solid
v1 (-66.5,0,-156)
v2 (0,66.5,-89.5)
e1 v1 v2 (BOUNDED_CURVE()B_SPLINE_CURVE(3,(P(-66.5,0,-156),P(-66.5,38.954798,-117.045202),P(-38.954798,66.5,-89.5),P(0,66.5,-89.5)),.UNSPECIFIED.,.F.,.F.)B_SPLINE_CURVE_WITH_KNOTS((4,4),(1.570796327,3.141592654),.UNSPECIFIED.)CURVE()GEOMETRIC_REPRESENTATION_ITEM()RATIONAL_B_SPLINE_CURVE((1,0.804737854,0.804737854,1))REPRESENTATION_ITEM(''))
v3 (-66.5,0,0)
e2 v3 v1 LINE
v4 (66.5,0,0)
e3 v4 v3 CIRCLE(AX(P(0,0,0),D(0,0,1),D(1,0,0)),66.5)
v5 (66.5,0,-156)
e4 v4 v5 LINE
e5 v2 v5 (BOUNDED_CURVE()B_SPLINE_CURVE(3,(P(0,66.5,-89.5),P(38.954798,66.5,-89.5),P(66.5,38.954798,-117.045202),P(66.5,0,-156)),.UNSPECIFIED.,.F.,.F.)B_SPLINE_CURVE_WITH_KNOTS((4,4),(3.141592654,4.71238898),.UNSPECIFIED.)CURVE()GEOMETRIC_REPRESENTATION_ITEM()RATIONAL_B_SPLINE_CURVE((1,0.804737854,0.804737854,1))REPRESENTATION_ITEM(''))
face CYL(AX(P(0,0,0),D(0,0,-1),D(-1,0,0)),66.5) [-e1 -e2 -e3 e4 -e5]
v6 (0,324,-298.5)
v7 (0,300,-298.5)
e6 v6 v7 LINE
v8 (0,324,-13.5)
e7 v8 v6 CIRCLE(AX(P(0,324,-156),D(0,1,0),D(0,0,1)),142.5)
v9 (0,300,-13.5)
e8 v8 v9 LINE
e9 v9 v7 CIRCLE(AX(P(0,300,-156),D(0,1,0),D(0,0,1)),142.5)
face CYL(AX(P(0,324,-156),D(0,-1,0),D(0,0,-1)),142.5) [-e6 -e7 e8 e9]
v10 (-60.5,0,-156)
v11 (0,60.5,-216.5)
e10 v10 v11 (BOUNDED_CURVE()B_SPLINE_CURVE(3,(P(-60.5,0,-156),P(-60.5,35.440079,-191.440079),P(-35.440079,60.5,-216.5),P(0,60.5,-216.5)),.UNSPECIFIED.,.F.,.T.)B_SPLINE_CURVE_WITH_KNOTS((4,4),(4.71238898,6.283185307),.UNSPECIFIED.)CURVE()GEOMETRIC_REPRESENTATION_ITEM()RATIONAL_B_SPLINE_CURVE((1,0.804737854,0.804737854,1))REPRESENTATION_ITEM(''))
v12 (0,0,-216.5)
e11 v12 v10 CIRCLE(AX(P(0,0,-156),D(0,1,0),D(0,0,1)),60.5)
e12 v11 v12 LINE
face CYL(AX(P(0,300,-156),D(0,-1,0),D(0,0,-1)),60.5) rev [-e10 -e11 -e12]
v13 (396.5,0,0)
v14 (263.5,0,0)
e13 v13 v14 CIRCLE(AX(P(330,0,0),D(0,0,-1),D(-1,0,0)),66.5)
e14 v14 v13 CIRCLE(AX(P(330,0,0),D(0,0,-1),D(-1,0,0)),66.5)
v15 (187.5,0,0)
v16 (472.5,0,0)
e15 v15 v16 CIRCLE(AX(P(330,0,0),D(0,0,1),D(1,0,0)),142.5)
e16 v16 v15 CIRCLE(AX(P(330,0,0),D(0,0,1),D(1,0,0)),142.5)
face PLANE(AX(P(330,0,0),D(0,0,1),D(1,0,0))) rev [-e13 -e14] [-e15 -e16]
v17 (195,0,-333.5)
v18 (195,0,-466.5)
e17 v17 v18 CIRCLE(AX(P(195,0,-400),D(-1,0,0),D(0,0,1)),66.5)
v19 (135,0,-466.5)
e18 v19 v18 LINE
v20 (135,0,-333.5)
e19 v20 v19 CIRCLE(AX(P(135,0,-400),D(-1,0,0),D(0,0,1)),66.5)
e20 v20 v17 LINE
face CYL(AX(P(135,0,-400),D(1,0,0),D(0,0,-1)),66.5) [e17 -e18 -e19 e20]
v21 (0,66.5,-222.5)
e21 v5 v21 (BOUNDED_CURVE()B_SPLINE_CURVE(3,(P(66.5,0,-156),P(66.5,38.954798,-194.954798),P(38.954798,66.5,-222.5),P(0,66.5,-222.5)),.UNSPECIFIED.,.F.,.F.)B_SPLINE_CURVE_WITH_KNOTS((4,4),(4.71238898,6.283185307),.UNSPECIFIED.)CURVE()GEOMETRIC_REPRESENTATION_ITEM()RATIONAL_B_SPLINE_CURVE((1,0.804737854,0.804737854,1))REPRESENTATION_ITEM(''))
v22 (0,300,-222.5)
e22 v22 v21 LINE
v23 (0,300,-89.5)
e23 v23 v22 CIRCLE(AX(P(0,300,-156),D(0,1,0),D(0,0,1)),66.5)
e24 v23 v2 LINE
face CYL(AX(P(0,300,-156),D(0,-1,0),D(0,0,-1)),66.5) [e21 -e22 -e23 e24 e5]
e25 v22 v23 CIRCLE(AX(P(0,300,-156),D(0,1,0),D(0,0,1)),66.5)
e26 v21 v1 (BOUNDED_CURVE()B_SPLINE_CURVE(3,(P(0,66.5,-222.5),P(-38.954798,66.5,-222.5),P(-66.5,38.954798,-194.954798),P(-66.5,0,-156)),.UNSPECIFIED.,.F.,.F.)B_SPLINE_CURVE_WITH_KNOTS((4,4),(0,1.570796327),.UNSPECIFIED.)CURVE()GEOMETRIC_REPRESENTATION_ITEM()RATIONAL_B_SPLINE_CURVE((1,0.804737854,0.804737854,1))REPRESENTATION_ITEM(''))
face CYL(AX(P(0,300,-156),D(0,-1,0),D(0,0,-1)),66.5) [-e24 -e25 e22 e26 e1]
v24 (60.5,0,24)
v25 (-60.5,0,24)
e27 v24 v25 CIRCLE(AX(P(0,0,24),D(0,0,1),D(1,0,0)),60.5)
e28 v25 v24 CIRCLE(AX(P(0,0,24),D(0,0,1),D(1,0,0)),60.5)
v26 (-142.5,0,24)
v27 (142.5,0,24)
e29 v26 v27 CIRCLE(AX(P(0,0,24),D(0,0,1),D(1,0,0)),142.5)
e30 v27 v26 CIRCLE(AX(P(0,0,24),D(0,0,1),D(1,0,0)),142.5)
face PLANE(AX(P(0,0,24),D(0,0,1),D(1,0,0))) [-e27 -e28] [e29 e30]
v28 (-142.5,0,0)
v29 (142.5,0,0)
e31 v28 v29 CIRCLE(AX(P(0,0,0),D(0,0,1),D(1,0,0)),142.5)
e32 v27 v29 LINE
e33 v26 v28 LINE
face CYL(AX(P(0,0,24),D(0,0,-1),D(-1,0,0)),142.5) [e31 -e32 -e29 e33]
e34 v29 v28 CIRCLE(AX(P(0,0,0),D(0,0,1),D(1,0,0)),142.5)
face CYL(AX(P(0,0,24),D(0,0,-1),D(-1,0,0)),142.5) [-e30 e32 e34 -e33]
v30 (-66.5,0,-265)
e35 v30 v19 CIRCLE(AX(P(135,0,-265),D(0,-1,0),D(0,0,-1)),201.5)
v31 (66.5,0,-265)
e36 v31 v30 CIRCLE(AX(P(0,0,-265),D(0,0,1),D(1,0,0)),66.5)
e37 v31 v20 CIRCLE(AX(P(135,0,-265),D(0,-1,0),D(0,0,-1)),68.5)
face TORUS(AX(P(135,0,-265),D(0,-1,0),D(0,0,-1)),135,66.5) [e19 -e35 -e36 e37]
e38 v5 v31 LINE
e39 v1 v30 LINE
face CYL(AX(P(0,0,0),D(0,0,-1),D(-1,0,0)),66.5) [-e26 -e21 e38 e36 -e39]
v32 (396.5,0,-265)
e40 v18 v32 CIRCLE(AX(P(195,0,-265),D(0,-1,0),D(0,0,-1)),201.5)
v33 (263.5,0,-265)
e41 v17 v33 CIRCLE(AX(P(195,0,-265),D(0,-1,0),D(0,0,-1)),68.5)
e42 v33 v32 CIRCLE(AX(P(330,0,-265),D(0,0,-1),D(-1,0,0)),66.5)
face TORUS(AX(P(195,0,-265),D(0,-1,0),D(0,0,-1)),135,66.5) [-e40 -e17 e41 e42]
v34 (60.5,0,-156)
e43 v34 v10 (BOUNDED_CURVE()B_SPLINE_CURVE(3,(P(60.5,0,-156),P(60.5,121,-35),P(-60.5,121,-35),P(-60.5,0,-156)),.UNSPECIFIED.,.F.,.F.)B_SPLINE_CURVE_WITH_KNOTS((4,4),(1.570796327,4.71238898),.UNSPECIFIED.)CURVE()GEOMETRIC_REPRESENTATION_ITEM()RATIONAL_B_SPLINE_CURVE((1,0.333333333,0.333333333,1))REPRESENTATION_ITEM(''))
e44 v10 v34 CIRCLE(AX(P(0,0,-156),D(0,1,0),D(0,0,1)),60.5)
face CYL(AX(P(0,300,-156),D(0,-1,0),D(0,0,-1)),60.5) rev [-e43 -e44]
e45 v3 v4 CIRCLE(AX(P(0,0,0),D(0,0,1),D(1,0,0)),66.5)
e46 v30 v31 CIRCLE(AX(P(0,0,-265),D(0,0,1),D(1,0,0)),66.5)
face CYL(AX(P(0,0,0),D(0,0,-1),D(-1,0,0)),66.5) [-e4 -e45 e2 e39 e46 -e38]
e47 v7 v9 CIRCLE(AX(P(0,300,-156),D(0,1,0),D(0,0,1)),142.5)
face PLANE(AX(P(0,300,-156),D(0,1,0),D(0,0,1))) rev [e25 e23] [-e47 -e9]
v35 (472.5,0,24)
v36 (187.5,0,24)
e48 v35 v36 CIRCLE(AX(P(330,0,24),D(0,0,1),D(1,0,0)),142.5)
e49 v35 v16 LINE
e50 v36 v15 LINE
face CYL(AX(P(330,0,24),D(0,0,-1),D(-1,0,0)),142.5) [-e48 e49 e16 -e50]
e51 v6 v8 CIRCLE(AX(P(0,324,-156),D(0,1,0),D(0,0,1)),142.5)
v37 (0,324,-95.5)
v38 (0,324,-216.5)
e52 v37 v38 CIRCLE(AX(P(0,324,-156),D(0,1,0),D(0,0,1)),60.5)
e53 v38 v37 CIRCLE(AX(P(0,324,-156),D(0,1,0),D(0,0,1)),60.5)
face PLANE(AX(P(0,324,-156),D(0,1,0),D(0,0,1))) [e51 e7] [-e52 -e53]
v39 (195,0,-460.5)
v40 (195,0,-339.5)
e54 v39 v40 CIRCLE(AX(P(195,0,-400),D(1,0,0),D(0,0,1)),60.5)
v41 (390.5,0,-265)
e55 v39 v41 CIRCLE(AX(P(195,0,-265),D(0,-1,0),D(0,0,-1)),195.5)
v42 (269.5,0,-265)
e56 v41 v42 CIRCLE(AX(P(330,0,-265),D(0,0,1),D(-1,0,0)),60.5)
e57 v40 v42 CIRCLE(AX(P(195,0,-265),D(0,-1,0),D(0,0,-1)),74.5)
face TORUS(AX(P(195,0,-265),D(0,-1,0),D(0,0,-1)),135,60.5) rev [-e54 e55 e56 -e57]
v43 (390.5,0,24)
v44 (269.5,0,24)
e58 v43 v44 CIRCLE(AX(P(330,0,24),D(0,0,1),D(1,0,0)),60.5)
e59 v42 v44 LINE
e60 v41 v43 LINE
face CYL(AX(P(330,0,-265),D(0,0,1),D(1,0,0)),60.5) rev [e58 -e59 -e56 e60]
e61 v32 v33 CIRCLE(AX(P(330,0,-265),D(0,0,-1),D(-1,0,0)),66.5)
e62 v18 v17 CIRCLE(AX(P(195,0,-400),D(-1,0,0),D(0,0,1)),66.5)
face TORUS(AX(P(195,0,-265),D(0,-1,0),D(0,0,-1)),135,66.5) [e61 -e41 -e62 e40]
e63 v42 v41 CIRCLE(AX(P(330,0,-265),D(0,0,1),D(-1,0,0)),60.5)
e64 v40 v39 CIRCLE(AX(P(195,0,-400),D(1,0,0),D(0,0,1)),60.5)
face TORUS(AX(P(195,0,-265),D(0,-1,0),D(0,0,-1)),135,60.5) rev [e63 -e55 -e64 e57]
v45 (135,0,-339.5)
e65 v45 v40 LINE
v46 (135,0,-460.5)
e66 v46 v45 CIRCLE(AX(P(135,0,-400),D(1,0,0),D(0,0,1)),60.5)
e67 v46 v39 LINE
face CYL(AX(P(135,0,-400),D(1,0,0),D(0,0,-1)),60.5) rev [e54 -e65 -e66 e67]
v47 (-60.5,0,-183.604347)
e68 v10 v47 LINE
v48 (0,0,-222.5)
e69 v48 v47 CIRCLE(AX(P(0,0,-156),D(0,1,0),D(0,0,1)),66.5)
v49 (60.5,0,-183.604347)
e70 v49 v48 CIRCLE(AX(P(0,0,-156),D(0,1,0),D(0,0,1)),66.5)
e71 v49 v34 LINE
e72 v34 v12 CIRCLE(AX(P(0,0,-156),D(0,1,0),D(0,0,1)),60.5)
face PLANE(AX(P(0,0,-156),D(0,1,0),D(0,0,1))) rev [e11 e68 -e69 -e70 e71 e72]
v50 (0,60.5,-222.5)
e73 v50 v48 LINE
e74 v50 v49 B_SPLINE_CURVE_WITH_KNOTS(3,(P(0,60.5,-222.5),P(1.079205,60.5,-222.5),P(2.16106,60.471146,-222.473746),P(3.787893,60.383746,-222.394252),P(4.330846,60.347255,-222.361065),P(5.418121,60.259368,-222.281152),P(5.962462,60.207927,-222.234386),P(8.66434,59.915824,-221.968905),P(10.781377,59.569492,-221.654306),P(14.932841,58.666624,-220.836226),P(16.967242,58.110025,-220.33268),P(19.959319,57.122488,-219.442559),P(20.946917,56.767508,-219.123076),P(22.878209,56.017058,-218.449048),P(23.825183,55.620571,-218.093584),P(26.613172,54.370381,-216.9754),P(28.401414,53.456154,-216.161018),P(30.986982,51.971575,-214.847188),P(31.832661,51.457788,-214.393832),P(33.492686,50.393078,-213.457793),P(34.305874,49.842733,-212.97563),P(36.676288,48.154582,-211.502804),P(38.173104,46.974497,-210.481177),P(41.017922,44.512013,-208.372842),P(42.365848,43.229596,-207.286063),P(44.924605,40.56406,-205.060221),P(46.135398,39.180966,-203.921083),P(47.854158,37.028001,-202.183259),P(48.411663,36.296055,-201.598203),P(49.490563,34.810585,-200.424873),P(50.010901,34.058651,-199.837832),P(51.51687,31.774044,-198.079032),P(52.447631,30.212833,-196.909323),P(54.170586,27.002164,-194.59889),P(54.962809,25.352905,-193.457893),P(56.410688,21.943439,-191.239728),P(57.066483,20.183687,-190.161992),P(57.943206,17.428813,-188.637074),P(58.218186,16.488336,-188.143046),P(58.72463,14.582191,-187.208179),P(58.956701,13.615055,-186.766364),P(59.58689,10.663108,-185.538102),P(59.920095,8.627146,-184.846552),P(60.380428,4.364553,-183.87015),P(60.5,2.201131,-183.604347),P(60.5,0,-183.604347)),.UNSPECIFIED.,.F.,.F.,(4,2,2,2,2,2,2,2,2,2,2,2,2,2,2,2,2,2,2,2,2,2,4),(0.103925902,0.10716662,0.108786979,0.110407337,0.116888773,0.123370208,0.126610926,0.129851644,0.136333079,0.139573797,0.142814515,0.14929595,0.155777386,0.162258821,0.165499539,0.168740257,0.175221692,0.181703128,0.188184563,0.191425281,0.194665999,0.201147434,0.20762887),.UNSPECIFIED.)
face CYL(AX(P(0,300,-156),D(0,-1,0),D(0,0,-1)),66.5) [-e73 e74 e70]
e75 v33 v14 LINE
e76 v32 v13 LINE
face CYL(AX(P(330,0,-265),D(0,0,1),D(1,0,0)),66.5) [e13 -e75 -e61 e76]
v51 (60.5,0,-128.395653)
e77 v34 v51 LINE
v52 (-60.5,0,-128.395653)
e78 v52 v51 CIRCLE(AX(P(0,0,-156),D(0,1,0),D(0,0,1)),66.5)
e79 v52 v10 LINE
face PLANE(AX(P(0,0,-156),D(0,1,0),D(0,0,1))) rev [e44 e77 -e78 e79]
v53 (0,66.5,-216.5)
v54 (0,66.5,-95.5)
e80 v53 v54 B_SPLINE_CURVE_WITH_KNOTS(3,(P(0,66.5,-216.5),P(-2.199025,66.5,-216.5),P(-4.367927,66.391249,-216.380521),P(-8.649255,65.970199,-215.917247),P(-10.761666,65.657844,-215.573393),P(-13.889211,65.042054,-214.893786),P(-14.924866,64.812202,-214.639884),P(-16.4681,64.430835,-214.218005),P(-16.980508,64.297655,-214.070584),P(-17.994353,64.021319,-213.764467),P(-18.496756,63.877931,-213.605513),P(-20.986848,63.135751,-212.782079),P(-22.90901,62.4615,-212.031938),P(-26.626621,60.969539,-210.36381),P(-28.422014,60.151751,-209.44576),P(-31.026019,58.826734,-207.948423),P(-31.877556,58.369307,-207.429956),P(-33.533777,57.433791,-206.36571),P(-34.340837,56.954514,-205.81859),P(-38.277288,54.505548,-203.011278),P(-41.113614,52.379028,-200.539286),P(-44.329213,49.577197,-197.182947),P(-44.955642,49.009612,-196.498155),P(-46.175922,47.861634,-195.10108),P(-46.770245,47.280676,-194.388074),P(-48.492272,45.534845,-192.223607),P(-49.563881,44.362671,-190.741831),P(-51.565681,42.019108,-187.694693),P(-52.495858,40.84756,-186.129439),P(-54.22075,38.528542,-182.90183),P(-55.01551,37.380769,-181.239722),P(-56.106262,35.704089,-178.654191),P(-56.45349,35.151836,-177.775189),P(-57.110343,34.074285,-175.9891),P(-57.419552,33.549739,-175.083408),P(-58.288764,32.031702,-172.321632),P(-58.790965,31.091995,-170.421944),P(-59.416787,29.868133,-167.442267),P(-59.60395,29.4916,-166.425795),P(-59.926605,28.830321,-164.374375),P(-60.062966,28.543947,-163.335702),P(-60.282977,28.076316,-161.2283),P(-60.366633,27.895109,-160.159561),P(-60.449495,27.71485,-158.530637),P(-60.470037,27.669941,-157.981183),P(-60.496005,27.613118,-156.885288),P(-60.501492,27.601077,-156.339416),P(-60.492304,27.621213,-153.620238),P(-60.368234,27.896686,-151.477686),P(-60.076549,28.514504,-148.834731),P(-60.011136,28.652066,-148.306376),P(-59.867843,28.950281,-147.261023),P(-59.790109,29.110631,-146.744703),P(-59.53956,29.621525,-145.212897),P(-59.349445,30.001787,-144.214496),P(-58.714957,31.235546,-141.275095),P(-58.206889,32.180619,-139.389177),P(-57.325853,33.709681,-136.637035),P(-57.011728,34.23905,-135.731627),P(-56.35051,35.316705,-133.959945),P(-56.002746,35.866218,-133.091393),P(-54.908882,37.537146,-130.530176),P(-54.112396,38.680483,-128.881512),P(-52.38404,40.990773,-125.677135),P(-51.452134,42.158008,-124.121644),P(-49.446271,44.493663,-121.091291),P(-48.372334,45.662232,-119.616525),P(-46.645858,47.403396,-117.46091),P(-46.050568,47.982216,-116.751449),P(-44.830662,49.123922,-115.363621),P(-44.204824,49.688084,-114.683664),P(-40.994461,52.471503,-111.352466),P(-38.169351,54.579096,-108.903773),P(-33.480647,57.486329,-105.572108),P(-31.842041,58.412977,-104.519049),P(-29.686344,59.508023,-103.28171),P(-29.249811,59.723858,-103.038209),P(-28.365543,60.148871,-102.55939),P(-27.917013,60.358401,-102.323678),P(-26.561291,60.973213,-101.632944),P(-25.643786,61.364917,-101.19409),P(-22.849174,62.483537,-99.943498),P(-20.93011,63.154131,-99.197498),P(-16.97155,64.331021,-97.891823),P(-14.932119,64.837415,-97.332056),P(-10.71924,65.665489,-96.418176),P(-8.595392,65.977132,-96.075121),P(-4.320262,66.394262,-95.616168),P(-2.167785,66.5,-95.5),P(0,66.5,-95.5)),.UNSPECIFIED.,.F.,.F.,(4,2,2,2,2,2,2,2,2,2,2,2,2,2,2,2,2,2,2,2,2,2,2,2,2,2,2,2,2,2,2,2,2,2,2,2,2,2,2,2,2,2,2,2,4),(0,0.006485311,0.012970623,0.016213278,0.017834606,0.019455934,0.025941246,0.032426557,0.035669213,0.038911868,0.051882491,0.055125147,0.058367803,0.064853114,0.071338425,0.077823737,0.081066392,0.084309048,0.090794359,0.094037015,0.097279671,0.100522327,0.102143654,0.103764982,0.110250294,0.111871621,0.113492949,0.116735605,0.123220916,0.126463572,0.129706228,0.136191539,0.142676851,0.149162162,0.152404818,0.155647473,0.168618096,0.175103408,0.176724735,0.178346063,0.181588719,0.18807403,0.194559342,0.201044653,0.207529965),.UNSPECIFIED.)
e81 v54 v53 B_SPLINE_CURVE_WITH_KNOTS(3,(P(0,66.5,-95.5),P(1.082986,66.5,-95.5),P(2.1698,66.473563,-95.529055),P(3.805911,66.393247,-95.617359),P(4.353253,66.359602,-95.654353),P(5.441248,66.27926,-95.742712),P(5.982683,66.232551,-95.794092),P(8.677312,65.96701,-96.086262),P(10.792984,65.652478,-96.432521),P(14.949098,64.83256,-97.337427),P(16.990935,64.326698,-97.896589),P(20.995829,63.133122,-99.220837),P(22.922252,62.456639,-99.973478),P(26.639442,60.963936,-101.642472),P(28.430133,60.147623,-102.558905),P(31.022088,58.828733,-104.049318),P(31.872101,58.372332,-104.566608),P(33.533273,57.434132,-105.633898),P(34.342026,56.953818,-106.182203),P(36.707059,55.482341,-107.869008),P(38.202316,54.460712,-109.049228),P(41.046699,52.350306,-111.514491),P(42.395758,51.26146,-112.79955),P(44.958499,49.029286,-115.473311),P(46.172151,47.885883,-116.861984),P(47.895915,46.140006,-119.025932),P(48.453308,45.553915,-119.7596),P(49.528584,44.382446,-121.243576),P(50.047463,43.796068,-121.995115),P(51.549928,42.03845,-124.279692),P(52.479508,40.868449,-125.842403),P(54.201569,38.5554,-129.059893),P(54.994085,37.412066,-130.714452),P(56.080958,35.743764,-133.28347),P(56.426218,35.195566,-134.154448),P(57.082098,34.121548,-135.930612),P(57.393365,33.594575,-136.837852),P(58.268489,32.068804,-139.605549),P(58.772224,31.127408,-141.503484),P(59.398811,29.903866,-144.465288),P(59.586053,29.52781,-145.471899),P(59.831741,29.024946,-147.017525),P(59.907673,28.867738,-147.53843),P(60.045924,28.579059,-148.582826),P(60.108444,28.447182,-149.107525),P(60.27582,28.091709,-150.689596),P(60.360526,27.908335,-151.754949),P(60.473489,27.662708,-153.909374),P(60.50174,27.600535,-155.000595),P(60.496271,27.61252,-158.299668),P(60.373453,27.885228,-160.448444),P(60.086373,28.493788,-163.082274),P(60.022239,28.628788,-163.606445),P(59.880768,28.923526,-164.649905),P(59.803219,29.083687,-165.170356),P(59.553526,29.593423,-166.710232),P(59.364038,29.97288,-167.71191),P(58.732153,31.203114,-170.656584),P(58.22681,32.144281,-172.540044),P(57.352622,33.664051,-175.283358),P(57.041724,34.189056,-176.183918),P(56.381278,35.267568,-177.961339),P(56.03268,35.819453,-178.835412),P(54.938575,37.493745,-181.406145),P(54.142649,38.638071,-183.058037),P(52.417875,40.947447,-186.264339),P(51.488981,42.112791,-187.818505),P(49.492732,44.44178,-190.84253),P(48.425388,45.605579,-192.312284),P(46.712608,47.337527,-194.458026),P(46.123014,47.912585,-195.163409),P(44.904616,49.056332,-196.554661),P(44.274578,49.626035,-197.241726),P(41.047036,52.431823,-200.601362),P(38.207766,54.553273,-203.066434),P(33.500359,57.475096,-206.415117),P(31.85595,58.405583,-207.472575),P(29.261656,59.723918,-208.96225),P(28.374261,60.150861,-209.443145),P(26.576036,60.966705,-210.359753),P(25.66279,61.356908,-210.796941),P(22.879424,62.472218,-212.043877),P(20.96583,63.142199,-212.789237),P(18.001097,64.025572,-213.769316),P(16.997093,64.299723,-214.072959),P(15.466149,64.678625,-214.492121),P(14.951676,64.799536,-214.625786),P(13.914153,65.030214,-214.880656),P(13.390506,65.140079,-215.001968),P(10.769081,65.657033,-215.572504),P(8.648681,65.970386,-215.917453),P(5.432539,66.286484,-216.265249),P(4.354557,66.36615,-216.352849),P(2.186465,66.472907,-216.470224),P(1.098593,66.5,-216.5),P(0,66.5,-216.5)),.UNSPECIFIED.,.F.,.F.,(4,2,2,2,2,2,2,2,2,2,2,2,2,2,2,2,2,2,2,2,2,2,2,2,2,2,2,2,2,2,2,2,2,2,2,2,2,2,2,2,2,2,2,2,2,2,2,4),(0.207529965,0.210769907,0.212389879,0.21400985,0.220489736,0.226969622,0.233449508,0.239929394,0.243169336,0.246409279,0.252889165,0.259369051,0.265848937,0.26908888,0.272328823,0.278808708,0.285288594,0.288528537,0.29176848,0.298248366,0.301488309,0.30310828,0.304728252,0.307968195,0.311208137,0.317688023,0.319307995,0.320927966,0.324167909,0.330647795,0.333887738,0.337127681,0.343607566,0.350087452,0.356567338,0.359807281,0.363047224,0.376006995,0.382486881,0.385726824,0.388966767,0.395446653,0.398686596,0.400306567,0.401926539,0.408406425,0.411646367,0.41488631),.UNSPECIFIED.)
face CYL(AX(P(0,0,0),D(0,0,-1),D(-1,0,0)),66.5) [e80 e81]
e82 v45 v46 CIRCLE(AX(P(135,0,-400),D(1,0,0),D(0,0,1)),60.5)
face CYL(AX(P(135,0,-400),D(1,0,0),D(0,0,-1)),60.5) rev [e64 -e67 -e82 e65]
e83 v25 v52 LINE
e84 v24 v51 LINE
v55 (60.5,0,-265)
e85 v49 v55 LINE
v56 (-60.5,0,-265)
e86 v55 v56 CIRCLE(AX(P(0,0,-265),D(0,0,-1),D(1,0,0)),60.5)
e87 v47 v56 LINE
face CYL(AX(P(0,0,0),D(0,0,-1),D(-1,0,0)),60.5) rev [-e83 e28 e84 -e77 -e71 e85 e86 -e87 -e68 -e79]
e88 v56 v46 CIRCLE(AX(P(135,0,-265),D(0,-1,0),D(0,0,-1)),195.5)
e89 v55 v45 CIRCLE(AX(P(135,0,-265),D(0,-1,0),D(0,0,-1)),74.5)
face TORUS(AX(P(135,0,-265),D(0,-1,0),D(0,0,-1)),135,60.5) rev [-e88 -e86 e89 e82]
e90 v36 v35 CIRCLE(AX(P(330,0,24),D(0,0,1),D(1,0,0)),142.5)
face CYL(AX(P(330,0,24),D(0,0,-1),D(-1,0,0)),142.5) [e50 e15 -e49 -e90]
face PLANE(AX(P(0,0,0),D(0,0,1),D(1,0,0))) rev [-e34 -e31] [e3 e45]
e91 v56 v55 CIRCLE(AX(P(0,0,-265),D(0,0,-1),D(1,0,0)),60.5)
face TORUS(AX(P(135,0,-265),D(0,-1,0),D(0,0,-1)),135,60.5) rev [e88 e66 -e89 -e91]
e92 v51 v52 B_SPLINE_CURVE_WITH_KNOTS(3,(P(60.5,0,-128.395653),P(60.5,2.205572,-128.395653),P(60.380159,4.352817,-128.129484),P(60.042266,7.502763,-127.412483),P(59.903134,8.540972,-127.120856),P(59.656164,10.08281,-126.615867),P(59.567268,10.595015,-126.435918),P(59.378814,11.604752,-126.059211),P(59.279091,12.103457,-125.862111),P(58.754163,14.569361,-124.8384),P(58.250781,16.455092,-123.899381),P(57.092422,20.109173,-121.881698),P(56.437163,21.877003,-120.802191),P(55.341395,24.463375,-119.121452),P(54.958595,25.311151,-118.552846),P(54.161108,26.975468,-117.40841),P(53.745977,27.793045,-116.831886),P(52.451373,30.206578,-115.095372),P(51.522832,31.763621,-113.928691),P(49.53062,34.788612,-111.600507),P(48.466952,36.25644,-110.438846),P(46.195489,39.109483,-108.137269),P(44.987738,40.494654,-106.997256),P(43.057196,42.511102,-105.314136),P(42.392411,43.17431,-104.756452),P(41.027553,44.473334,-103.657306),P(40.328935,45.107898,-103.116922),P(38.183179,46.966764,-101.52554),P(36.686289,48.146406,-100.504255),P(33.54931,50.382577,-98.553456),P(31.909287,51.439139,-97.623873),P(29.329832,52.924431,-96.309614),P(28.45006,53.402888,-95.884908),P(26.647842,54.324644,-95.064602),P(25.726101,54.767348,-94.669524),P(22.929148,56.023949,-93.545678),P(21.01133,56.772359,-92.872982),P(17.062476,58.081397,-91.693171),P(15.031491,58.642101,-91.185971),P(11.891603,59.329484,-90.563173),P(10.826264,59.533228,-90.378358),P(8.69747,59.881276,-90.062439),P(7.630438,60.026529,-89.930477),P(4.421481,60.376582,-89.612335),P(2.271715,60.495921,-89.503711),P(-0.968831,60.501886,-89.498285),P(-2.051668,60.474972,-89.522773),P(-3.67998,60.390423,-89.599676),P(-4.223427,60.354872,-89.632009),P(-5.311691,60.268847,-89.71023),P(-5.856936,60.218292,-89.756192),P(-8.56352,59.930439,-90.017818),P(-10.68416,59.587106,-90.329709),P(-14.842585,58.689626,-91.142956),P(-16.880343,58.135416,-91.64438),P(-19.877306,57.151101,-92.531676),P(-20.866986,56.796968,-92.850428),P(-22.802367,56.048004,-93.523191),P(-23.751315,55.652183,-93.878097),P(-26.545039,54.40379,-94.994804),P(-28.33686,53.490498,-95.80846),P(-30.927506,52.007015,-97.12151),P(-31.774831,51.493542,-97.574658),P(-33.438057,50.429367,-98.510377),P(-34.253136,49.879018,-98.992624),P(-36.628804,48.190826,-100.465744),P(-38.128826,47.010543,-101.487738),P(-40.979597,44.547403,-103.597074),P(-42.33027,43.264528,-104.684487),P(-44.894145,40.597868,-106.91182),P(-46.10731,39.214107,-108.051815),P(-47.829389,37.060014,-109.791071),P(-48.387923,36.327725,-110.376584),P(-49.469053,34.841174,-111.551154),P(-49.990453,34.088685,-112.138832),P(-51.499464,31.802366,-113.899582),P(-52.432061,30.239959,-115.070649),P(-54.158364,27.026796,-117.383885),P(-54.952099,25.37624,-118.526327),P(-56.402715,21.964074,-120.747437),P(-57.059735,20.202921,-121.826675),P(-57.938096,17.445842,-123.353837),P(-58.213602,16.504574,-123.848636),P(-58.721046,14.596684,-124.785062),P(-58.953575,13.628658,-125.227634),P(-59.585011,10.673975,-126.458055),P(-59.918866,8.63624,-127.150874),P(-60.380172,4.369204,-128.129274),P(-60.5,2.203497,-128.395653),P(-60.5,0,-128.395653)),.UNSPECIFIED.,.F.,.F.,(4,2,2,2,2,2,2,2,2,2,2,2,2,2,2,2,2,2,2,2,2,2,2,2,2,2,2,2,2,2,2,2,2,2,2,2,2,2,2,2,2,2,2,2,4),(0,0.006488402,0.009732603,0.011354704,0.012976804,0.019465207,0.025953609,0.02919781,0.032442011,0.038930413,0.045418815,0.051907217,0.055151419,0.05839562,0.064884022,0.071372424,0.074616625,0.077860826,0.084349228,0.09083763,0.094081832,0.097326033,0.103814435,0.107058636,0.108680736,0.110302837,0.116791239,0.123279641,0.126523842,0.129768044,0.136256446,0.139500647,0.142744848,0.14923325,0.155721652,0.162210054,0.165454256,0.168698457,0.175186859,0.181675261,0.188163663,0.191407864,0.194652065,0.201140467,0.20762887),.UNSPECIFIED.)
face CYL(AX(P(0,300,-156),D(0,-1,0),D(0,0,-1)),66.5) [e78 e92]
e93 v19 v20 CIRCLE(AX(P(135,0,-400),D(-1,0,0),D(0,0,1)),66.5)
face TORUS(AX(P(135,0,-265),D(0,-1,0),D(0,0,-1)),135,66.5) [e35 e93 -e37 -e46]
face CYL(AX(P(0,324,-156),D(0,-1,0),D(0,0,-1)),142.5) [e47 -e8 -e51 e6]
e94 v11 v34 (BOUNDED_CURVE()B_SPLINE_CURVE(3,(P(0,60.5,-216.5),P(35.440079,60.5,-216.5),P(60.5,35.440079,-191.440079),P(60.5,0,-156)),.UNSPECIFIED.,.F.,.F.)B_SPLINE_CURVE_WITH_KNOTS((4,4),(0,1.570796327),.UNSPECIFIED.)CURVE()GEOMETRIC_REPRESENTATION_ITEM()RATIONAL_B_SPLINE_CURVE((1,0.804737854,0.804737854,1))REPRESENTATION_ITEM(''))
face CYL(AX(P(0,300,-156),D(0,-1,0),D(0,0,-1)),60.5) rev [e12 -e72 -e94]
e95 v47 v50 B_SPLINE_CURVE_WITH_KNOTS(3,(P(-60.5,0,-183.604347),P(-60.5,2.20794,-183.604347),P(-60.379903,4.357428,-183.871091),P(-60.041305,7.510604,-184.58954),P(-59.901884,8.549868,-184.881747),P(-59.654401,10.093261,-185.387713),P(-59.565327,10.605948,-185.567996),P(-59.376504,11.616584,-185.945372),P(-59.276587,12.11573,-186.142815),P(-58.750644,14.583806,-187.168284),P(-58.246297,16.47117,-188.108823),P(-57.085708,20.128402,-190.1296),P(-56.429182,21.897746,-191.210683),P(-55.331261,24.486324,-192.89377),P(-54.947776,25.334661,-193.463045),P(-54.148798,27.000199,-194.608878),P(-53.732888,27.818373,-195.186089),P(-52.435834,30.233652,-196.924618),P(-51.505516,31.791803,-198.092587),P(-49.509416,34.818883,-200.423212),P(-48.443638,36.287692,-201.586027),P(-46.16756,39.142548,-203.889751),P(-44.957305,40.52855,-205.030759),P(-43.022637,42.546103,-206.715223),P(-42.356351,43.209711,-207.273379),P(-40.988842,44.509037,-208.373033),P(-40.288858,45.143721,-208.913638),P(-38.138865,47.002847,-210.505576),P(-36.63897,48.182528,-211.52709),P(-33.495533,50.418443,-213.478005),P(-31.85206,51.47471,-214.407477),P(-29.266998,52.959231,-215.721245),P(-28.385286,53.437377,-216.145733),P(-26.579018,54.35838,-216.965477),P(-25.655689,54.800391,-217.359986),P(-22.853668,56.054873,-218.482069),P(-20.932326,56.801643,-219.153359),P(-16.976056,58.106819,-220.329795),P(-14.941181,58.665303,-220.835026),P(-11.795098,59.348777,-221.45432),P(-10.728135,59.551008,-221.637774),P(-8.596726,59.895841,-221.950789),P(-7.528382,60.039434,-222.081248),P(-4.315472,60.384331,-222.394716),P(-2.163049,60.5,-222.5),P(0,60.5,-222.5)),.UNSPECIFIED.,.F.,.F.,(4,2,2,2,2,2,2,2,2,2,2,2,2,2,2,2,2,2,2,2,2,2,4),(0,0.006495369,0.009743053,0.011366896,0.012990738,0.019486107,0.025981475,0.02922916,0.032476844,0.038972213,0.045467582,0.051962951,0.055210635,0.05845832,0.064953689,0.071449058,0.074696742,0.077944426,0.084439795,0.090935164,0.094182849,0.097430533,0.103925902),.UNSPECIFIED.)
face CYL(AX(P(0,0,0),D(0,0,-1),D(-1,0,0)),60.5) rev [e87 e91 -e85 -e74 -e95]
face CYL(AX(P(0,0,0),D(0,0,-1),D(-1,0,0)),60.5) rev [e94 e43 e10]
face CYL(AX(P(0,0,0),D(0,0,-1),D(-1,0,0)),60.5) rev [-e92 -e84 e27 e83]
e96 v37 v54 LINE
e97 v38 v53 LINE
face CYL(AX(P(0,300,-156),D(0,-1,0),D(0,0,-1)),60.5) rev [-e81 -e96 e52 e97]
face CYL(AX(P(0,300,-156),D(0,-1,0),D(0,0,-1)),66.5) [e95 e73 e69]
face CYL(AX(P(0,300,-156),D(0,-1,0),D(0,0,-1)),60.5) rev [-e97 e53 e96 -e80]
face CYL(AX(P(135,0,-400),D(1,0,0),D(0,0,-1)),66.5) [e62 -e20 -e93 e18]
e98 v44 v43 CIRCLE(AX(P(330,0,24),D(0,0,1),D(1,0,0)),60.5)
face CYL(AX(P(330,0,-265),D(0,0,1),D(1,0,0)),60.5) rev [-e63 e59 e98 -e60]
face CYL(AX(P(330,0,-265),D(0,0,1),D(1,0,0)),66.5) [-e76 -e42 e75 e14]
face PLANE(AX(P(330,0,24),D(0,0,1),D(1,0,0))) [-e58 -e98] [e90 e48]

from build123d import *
from build123d.topology import SkipClean

# Parameters (mm, degrees)
SKETCH1_R           = 66.5
SKETCH1_R_2         = 60.5
SKETCH3_R           = 142.5
SKETCH3_R_2         = 60.5
BOSS_EXTRUDE1_DEPTH = 24
SKETCH4_R           = 66.5
SKETCH4_R_2         = 60.5
BOSS_EXTRUDE2_DEPTH = 300
SKETCH5_R           = 142.5
SKETCH5_R_2         = 60.5
BOSS_EXTRUDE3_DEPTH = 24


with BuildPart() as part:
    # Sweep1: sweep along a path in Sketch2
    with BuildLine(Plane(origin=(0, 0, 0), x_dir=(1, 0, 0), z_dir=(0, 1, 0))) as sweep1_path:
        Line((0, 0), (0, 265))
        ThreePointArc((0, 265), (39.54058454, 360.45941546), (135, 400))
        Line((135, 400), (195, 400))
        ThreePointArc((195, 400), (290.45941546, 360.45941546), (330, 265))
        Line((330, 265), (330, 0))
    # Sketch1 → Sweep1 (sweep)
    with BuildSketch(Plane.XY):
        Circle(SKETCH1_R)
        Circle(SKETCH1_R_2, mode=Mode.SUBTRACT)
    sweep(path=sweep1_path.line)

    # Sketch3 → Boss-Extrude1 (add)
    # profile 1 of 2: a face of its own
    with SkipClean():  # the faces are left unmerged after this step: merging them gives an invalid solid
        with BuildSketch(Plane.XY):
            with Locations((330, 0)):
                Circle(SKETCH3_R)
            with Locations((330, 0)):
                Circle(SKETCH3_R_2, mode=Mode.SUBTRACT)
        # profile 2 of 2: a face of its own
        with BuildSketch(Plane.XY):
            Circle(SKETCH3_R)
            with Locations(Location((0, 0, 0), (0, 0, 180))):
                Circle(SKETCH3_R_2, mode=Mode.SUBTRACT)
        extrude(amount=BOSS_EXTRUDE1_DEPTH)

    # Sketch4 → Boss-Extrude2 (add)
    with SkipClean():  # the faces are left unmerged after this step: merging them gives an invalid solid
        with BuildSketch(Plane(origin=(0, 0, 0), x_dir=(1, 0, 0), z_dir=(0, 1, 0))):
            with Locations((0, 156)):
                Circle(SKETCH4_R)
            with Locations(Location((0, 156, 0), (0, 0, 90))):
                Circle(SKETCH4_R_2, mode=Mode.SUBTRACT)
        extrude(amount=BOSS_EXTRUDE2_DEPTH)

    # Sketch5 → Boss-Extrude3 (add)
    with SkipClean():  # the faces are left unmerged after this step: merging them gives an invalid solid
        with BuildSketch(Plane(origin=(0, 300, 0), x_dir=(1, 0, 0), z_dir=(0, 1, 0))):
            with Locations(Location((0, 156, 0), (0, 0, 270))):
                Circle(SKETCH5_R)
            with Locations(Location((0, 156, 0), (0, 0, 90))):
                Circle(SKETCH5_R_2, mode=Mode.SUBTRACT)
        extrude(amount=BOSS_EXTRUDE3_DEPTH)


solid = part.part
